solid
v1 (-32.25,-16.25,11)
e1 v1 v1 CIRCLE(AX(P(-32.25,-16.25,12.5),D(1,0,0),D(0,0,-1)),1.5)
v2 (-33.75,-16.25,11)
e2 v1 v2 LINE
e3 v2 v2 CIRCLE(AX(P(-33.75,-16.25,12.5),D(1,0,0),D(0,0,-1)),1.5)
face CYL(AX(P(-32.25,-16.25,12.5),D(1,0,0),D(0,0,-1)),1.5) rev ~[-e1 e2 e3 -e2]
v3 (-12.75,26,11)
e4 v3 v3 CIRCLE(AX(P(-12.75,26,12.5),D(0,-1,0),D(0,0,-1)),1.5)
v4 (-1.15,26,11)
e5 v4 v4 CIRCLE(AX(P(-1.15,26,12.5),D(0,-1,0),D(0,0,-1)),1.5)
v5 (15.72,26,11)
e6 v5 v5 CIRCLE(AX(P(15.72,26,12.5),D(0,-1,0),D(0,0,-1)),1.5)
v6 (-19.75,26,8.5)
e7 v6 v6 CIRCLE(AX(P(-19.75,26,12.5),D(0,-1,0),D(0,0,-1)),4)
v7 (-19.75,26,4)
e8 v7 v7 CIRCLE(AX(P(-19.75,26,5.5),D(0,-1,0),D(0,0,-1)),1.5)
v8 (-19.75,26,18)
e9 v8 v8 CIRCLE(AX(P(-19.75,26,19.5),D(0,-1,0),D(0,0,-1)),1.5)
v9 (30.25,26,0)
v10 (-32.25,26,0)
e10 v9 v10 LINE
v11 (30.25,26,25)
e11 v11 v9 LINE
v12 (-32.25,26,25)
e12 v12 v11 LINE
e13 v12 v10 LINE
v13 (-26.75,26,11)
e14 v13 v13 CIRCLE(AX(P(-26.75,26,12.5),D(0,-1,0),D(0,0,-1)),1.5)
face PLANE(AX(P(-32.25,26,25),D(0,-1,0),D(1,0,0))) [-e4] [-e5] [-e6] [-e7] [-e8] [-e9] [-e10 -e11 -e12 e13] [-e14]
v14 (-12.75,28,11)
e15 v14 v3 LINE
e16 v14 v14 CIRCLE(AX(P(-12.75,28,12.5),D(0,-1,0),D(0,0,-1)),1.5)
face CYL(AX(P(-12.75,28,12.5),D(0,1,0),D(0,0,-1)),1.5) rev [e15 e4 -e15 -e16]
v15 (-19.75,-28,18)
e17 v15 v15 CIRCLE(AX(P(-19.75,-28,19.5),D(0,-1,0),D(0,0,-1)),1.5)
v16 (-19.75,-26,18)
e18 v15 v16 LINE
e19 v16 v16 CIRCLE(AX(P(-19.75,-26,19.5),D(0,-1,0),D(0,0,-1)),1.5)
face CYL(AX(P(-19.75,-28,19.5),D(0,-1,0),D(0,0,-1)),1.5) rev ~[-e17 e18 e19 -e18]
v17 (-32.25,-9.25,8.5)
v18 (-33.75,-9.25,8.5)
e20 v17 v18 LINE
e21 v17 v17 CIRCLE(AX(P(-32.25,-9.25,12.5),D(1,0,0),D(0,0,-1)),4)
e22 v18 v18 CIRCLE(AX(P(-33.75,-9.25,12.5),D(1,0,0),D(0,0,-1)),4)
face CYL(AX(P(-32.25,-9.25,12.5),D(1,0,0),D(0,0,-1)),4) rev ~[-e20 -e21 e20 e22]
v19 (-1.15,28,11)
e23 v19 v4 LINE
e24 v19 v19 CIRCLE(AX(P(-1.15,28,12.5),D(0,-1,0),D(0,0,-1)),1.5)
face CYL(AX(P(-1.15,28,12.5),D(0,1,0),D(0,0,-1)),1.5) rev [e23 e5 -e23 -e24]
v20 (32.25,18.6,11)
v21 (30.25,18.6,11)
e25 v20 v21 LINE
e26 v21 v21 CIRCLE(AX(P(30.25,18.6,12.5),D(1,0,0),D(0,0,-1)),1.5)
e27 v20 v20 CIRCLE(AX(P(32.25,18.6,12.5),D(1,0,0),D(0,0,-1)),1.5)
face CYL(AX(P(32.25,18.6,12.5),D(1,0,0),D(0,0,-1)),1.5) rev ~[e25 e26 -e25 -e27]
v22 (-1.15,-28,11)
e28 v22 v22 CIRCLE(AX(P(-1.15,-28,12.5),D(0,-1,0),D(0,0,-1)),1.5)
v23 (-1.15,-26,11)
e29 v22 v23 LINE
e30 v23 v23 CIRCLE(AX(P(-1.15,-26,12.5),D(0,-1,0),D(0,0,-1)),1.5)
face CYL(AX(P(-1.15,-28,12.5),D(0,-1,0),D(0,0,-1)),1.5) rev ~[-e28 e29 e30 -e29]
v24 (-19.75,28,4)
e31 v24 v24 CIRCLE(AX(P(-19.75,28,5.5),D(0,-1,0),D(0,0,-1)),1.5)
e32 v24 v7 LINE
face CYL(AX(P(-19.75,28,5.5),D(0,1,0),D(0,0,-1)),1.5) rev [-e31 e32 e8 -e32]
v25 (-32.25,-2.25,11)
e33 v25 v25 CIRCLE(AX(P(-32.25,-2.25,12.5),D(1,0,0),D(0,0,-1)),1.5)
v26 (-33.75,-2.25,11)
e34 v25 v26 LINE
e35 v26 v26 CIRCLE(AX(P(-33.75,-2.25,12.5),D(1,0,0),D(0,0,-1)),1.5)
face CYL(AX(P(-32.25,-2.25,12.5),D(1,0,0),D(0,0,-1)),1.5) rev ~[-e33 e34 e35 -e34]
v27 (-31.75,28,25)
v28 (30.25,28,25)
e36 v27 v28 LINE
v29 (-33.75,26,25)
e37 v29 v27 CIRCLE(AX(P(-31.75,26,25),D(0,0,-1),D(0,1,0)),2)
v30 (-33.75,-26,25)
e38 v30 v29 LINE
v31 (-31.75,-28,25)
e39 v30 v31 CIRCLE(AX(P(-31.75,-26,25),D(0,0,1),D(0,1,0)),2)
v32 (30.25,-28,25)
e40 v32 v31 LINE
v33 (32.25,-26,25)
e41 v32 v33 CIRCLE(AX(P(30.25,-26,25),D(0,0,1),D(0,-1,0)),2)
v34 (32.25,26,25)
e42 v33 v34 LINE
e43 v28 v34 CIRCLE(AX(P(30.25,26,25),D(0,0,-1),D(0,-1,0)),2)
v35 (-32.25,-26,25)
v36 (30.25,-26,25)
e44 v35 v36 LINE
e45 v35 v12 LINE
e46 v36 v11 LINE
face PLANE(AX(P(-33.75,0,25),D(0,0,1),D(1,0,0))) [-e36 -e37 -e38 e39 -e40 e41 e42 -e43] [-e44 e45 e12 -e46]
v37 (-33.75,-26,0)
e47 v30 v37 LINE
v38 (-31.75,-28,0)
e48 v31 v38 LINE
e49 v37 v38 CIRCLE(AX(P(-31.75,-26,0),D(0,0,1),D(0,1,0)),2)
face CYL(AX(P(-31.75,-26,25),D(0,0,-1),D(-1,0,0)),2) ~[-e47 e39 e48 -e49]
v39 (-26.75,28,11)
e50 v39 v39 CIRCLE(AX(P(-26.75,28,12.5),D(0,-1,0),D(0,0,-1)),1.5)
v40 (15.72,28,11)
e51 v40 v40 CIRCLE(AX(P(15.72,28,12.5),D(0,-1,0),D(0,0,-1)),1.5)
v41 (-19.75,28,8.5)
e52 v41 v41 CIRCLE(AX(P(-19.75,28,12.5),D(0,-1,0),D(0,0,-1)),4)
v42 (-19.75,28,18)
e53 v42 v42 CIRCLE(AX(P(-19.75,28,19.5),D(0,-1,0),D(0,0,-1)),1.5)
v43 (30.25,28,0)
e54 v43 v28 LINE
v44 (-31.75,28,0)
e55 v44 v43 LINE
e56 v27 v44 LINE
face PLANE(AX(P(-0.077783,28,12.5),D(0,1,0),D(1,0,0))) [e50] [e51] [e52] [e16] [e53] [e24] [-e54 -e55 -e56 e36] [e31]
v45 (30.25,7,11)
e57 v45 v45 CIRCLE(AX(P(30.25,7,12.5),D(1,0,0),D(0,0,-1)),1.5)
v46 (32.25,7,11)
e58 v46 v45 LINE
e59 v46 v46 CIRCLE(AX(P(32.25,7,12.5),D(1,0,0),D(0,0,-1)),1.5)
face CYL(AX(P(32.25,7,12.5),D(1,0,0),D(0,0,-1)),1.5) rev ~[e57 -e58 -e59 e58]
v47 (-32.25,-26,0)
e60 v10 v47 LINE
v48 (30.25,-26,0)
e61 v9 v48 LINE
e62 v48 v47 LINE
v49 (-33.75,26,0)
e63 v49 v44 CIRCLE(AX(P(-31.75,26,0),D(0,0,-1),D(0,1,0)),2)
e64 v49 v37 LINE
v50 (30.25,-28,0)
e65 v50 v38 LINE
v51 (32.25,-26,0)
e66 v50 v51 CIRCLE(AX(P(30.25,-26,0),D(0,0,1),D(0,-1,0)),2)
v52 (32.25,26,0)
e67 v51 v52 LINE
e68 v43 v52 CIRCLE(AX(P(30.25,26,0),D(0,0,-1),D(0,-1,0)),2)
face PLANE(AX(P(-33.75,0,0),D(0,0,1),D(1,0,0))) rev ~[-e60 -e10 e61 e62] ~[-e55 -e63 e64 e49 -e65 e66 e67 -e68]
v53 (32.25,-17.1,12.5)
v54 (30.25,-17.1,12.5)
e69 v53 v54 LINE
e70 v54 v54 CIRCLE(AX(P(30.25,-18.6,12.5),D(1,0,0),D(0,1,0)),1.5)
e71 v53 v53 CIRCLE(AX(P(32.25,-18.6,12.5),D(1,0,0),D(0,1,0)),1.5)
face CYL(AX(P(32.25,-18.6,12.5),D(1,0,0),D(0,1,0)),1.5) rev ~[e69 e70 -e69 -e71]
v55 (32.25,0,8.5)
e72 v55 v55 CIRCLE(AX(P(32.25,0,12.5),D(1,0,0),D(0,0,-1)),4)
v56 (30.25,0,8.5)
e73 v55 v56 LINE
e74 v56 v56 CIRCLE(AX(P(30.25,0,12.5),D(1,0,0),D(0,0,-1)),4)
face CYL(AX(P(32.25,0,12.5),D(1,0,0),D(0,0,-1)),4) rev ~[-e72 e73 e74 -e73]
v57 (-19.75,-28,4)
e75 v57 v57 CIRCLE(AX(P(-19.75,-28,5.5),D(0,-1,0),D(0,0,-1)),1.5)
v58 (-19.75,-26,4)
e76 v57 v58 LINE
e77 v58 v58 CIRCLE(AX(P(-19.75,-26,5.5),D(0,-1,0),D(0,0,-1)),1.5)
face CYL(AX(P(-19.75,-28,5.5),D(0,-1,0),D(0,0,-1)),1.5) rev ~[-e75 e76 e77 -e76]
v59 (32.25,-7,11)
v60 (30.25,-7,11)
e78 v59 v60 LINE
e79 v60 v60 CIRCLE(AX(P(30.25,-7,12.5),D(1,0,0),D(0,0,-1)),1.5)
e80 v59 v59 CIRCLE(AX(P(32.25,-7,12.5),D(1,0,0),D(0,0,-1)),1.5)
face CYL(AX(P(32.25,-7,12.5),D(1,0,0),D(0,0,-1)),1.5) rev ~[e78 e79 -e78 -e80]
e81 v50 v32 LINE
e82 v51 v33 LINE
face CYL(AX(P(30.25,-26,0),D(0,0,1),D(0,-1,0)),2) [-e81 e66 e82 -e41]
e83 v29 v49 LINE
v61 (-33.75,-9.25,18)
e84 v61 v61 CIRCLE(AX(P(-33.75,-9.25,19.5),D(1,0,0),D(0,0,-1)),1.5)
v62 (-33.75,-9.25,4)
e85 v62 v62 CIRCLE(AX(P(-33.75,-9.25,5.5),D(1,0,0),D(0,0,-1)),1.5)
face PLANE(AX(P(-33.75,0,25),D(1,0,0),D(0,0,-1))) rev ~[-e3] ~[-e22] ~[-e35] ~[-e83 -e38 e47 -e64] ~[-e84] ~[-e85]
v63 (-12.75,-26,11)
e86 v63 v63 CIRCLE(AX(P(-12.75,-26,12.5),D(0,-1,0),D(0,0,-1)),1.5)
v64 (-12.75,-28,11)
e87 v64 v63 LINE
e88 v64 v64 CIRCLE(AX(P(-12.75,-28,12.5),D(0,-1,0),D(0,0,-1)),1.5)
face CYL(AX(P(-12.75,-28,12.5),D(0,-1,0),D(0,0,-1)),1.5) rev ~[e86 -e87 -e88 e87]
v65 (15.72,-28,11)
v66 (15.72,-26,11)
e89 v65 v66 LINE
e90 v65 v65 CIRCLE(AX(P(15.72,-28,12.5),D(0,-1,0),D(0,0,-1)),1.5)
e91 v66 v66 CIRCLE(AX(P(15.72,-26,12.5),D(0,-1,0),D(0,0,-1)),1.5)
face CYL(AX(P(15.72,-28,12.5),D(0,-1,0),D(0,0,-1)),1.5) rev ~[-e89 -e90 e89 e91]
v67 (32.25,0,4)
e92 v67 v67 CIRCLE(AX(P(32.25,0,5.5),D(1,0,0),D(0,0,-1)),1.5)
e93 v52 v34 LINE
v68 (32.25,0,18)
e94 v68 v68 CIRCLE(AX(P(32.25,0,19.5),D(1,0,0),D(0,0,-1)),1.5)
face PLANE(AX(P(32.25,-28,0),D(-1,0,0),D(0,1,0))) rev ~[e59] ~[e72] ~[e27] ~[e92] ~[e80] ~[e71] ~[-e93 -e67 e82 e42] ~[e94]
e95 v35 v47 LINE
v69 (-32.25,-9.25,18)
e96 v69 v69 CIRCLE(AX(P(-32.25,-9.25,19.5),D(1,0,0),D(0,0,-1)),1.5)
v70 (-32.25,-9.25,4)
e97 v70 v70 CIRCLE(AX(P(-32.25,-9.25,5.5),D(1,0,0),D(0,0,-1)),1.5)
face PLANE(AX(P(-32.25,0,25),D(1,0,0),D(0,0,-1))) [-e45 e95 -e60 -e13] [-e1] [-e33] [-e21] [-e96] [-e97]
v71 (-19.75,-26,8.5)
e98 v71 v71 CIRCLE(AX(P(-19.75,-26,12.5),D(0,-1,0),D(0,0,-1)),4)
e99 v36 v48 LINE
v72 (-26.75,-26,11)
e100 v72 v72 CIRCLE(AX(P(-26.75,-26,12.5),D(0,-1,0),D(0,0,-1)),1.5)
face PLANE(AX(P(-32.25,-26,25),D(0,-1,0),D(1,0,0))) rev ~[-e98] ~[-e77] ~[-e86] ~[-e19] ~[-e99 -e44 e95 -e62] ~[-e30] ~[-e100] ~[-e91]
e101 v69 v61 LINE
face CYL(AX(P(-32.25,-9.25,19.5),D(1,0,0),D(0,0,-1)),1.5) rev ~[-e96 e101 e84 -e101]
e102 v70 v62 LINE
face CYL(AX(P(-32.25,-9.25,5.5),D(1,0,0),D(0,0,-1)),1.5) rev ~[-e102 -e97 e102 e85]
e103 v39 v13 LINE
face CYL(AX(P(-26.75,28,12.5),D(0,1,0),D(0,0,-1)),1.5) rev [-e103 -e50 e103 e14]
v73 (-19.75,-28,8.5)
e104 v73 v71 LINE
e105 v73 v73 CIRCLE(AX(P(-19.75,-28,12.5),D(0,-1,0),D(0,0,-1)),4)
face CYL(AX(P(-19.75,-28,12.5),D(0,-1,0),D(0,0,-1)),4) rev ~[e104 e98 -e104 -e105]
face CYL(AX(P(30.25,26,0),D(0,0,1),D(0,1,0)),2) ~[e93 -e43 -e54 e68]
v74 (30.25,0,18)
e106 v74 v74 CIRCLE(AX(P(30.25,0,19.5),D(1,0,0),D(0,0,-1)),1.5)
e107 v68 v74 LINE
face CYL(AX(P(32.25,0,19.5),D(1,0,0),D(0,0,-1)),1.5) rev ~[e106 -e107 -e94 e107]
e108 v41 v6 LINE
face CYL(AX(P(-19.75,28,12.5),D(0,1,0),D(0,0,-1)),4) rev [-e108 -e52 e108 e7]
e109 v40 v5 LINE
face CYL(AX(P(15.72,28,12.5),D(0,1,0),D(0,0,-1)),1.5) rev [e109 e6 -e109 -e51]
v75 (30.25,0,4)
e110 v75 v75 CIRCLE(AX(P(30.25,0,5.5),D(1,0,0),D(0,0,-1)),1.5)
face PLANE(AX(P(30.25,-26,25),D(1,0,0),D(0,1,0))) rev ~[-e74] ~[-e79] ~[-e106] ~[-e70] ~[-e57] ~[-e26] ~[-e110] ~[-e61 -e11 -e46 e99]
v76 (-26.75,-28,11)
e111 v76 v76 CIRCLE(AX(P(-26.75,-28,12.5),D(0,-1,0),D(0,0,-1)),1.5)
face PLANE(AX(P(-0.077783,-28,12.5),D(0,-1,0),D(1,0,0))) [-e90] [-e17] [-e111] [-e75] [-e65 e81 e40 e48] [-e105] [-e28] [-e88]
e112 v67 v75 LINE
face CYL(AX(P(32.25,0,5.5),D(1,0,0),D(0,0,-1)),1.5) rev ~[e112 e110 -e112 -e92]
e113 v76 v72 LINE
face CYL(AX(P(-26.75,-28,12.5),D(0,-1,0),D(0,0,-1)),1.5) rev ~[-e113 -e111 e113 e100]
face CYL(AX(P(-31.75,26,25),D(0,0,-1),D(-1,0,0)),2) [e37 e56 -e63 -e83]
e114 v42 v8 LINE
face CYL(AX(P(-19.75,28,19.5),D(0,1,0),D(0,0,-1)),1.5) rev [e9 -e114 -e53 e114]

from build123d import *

# Parameters (mm, degrees)
SKETCH1_W                       = 64.5
SKETCH1_H                       = 56
BOSS_EXTRUDE1_DEPTH             = 25
CUT_EXTRUDE1_REACH              = 51.488
SKETCH2_W                       = 62.5
SKETCH2_H                       = 52
CUT_EXTRUDE2_REACH              = 76.627
SKETCH3_R                       = 4
SKETCH3_R_2                     = 1.5
CUT_EXTRUDE3_REACH              = 71.29
SKETCH4_R                       = 4
SKETCH4_R_2                     = 1.5
FILLET3_R                       = 2
BOSS_EXTRUDE2_REACH             = 51.488
SKETCH5_W                       = 1.5
SKETCH5_H                       = 25
BOSS_EXTRUDE2_DIRECTION_2_REACH = 51.488
FILLET4_R                       = 2
SKETCH6_R                       = 1.5
SKETCH6_R_2                     = 4
CUT_EXTRUDE5_DEPTH              = 1.5


with BuildPart() as part:
    # Sketch1 → Boss-Extrude1 (new body)
    with BuildSketch(Plane.XY):
        Rectangle(SKETCH1_W, SKETCH1_H)
    extrude(amount=BOSS_EXTRUDE1_DEPTH)

    # Sketch2 → Cut-Extrude1 (cut, up to next)
    with BuildSketch(Plane.XY.offset(25), mode=Mode.PRIVATE) as cut_extrude1_sk1:
        with Locations((-1, 0)):
            Rectangle(SKETCH2_W, SKETCH2_H)
    cut_extrude1_tool1 = extrude(cut_extrude1_sk1.sketch, amount=-CUT_EXTRUDE1_REACH, mode=Mode.PRIVATE) & part.part
    add(cut_extrude1_tool1.solids().sort_by_distance((-1, 0, 25))[0], mode=Mode.SUBTRACT)

    # Sketch3 → Cut-Extrude2 (cut, up to next)
    with BuildSketch(Plane(origin=(32.25, 0, 0), x_dir=(0, 0, -1), z_dir=(1, 0, 0)), mode=Mode.PRIVATE) as cut_extrude2_sk1:
        with Locations((-12.5, 0)):
            Circle(SKETCH3_R)
    cut_extrude2_tool1 = extrude(cut_extrude2_sk1.sketch, amount=-CUT_EXTRUDE2_REACH, mode=Mode.PRIVATE) & part.part
    # Sketch3 → Cut-Extrude2 (cut, up to next)
    with BuildSketch(Plane(origin=(32.25, 0, 0), x_dir=(0, 0, -1), z_dir=(1, 0, 0)), mode=Mode.PRIVATE) as cut_extrude2_sk2:
        with Locations((-5.5, 0)):
            Circle(SKETCH3_R_2)
    cut_extrude2_tool2 = extrude(cut_extrude2_sk2.sketch, amount=-CUT_EXTRUDE2_REACH, mode=Mode.PRIVATE) & part.part
    # Sketch3 → Cut-Extrude2 (cut, up to next)
    with BuildSketch(Plane(origin=(32.25, 0, 0), x_dir=(0, 0, -1), z_dir=(1, 0, 0)), mode=Mode.PRIVATE) as cut_extrude2_sk3:
        with Locations((-12.5, 18.6)):
            Circle(SKETCH3_R_2)
    cut_extrude2_tool3 = extrude(cut_extrude2_sk3.sketch, amount=-CUT_EXTRUDE2_REACH, mode=Mode.PRIVATE) & part.part
    # Sketch3 → Cut-Extrude2 (cut, up to next)
    with BuildSketch(Plane(origin=(32.25, 0, 0), x_dir=(0, 0, -1), z_dir=(1, 0, 0)), mode=Mode.PRIVATE) as cut_extrude2_sk4:
        with Locations((-12.5, -7)):
            Circle(SKETCH3_R_2)
    cut_extrude2_tool4 = extrude(cut_extrude2_sk4.sketch, amount=-CUT_EXTRUDE2_REACH, mode=Mode.PRIVATE) & part.part
    # Sketch3 → Cut-Extrude2 (cut, up to next)
    with BuildSketch(Plane(origin=(32.25, 0, 0), x_dir=(0, 0, -1), z_dir=(1, 0, 0)), mode=Mode.PRIVATE) as cut_extrude2_sk5:
        with Locations((-19.5, 0)):
            Circle(SKETCH3_R_2)
    cut_extrude2_tool5 = extrude(cut_extrude2_sk5.sketch, amount=-CUT_EXTRUDE2_REACH, mode=Mode.PRIVATE) & part.part
    # Sketch3 → Cut-Extrude2 (cut, up to next)
    with BuildSketch(Plane(origin=(32.25, 0, 0), x_dir=(0, 0, -1), z_dir=(1, 0, 0)), mode=Mode.PRIVATE) as cut_extrude2_sk6:
        with Locations((-12.5, 7)):
            Circle(SKETCH3_R_2)
    cut_extrude2_tool6 = extrude(cut_extrude2_sk6.sketch, amount=-CUT_EXTRUDE2_REACH, mode=Mode.PRIVATE) & part.part
    # Sketch3 → Cut-Extrude2 (cut, up to next)
    with BuildSketch(Plane(origin=(32.25, 0, 0), x_dir=(0, 0, -1), z_dir=(1, 0, 0)), mode=Mode.PRIVATE) as cut_extrude2_sk7:
        with Locations(Location((-12.5, -18.6, 0), (0, 0, 90))):
            Circle(SKETCH3_R_2)
    cut_extrude2_tool7 = extrude(cut_extrude2_sk7.sketch, amount=-CUT_EXTRUDE2_REACH, mode=Mode.PRIVATE) & part.part
    add(cut_extrude2_tool1.solids().sort_by_distance((32.25, 0, 12.5))[0], mode=Mode.SUBTRACT)
    add(cut_extrude2_tool2.solids().sort_by_distance((32.25, 0, 5.5))[0], mode=Mode.SUBTRACT)
    add(cut_extrude2_tool3.solids().sort_by_distance((32.25, 18.6, 12.5))[0], mode=Mode.SUBTRACT)
    add(cut_extrude2_tool4.solids().sort_by_distance((32.25, -7, 12.5))[0], mode=Mode.SUBTRACT)
    add(cut_extrude2_tool5.solids().sort_by_distance((32.25, 0, 19.5))[0], mode=Mode.SUBTRACT)
    add(cut_extrude2_tool6.solids().sort_by_distance((32.25, 7, 12.5))[0], mode=Mode.SUBTRACT)
    add(cut_extrude2_tool7.solids().sort_by_distance((32.25, -18.6, 12.5))[0], mode=Mode.SUBTRACT)

    # Sketch4 → Cut-Extrude3 (cut, up to next)
    with BuildSketch(Plane.XZ.offset(28), mode=Mode.PRIVATE) as cut_extrude3_sk1:
        with Locations(Location((-19.75, 12.5, 0), (0, 0, 270))):
            Circle(SKETCH4_R)
    cut_extrude3_tool1 = extrude(cut_extrude3_sk1.sketch, amount=-CUT_EXTRUDE3_REACH, mode=Mode.PRIVATE) & part.part
    # Sketch4 → Cut-Extrude3 (cut, up to next)
    with BuildSketch(Plane.XZ.offset(28), mode=Mode.PRIVATE) as cut_extrude3_sk2:
        with Locations(Location((-12.75, 12.5, 0), (0, 0, 270))):
            Circle(SKETCH4_R_2)
    cut_extrude3_tool2 = extrude(cut_extrude3_sk2.sketch, amount=-CUT_EXTRUDE3_REACH, mode=Mode.PRIVATE) & part.part
    # Sketch4 → Cut-Extrude3 (cut, up to next)
    with BuildSketch(Plane.XZ.offset(28), mode=Mode.PRIVATE) as cut_extrude3_sk3:
        with Locations(Location((-1.15, 12.5, 0), (0, 0, 270))):
            Circle(SKETCH4_R_2)
    cut_extrude3_tool3 = extrude(cut_extrude3_sk3.sketch, amount=-CUT_EXTRUDE3_REACH, mode=Mode.PRIVATE) & part.part
    # Sketch4 → Cut-Extrude3 (cut, up to next)
    with BuildSketch(Plane.XZ.offset(28), mode=Mode.PRIVATE) as cut_extrude3_sk4:
        with Locations(Location((15.72, 12.5, 0), (0, 0, 270))):
            Circle(SKETCH4_R_2)
    cut_extrude3_tool4 = extrude(cut_extrude3_sk4.sketch, amount=-CUT_EXTRUDE3_REACH, mode=Mode.PRIVATE) & part.part
    # Sketch4 → Cut-Extrude3 (cut, up to next)
    with BuildSketch(Plane.XZ.offset(28), mode=Mode.PRIVATE) as cut_extrude3_sk5:
        with Locations(Location((-19.75, 5.5, 0), (0, 0, 270))):
            Circle(SKETCH4_R_2)
    cut_extrude3_tool5 = extrude(cut_extrude3_sk5.sketch, amount=-CUT_EXTRUDE3_REACH, mode=Mode.PRIVATE) & part.part
    # Sketch4 → Cut-Extrude3 (cut, up to next)
    with BuildSketch(Plane.XZ.offset(28), mode=Mode.PRIVATE) as cut_extrude3_sk6:
        with Locations(Location((-26.75, 12.5, 0), (0, 0, 270))):
            Circle(SKETCH4_R_2)
    cut_extrude3_tool6 = extrude(cut_extrude3_sk6.sketch, amount=-CUT_EXTRUDE3_REACH, mode=Mode.PRIVATE) & part.part
    # Sketch4 → Cut-Extrude3 (cut, up to next)
    with BuildSketch(Plane.XZ.offset(28), mode=Mode.PRIVATE) as cut_extrude3_sk7:
        with Locations(Location((-19.75, 19.5, 0), (0, 0, 270))):
            Circle(SKETCH4_R_2)
    cut_extrude3_tool7 = extrude(cut_extrude3_sk7.sketch, amount=-CUT_EXTRUDE3_REACH, mode=Mode.PRIVATE) & part.part
    cut_extrude3_1 = cut_extrude3_tool1.solids().sort_by_distance((-19.75, -28, 12.5))[0]
    add(cut_extrude3_1, mode=Mode.SUBTRACT)
    cut_extrude3_2 = cut_extrude3_tool2.solids().sort_by_distance((-12.75, -28, 12.5))[0]
    add(cut_extrude3_2, mode=Mode.SUBTRACT)
    cut_extrude3_3 = cut_extrude3_tool3.solids().sort_by_distance((-1.15, -28, 12.5))[0]
    add(cut_extrude3_3, mode=Mode.SUBTRACT)
    cut_extrude3_4 = cut_extrude3_tool4.solids().sort_by_distance((15.72, -28, 12.5))[0]
    add(cut_extrude3_4, mode=Mode.SUBTRACT)
    cut_extrude3_5 = cut_extrude3_tool5.solids().sort_by_distance((-19.75, -28, 5.5))[0]
    add(cut_extrude3_5, mode=Mode.SUBTRACT)
    cut_extrude3_6 = cut_extrude3_tool6.solids().sort_by_distance((-26.75, -28, 12.5))[0]
    add(cut_extrude3_6, mode=Mode.SUBTRACT)
    cut_extrude3_7 = cut_extrude3_tool7.solids().sort_by_distance((-19.75, -28, 19.5))[0]
    add(cut_extrude3_7, mode=Mode.SUBTRACT)
    cut_extrude3 = cut_extrude3_1 + cut_extrude3_2 + cut_extrude3_3 + cut_extrude3_4 + cut_extrude3_5 + cut_extrude3_6 + cut_extrude3_7  # Cut-Extrude3 as one shape, for the pattern or mirror that repeats it

    # Mirror1: Cut-Extrude3 across plane
    add(cut_extrude3.mirror(Plane.ZX), mode=Mode.SUBTRACT)

    # Fillet3
    fillet3_edges = [part.edges().sort_by_distance(p)[0] for p in [
        (32.25, -28, 12.5),
        (32.25, 28, 12.5),
    ]]
    fillet(fillet3_edges, radius=FILLET3_R)

    # Boss-Extrude2: up to this face of the body (flat: up to its plane)
    boss_extrude2_end = Plane(part.part.faces().sort_by_distance((-1, 28, 0.673145601))[0])
    # Sketch5 → Boss-Extrude2 (add, up to the picked face)
    with BuildSketch(Plane(origin=(0, 0, 0), x_dir=(1, 0, 0), z_dir=(0, 1, 0)), mode=Mode.PRIVATE) as boss_extrude2_sk1:
        with Locations((-33, -12.5)):
            Rectangle(SKETCH5_W, SKETCH5_H)
    boss_extrude2_tool1 = split(extrude(boss_extrude2_sk1.sketch, amount=BOSS_EXTRUDE2_REACH, mode=Mode.PRIVATE), bisect_by=boss_extrude2_end, keep=Keep.BOTH, mode=Mode.PRIVATE)
    add(boss_extrude2_tool1.solids().sort_by(Axis((-33, 0, 12.5), (0, 1, 0)))[0])

    # Boss-Extrude2 direction 2: up to this face of the body (flat: up to its plane)
    boss_extrude2_direction_2_end = Plane(part.part.faces().sort_by_distance((-1, -28, 0.673145601))[0])
    # Sketch5 → Boss-Extrude2 direction 2 (add, up to the picked face)
    with BuildSketch(Plane(origin=(0, 0, 0), x_dir=(1, 0, 0), z_dir=(0, 1, 0)), mode=Mode.PRIVATE) as boss_extrude2_direction_2_sk1:
        with Locations((-33, -12.5)):
            Rectangle(SKETCH5_W, SKETCH5_H)
    boss_extrude2_direction_2_tool1 = split(extrude(boss_extrude2_direction_2_sk1.sketch, amount=-BOSS_EXTRUDE2_DIRECTION_2_REACH, mode=Mode.PRIVATE), bisect_by=boss_extrude2_direction_2_end, keep=Keep.BOTH, mode=Mode.PRIVATE)
    add(boss_extrude2_direction_2_tool1.solids().sort_by(Axis((-33, 0, 12.5), (0, -1, 0)))[0])

    # Fillet4
    fillet4_edges = [part.edges().sort_by_distance(p)[0] for p in [
        (-33.75, 28, 12.5),
        (-33.75, -28, 12.5),
    ]]
    fillet(fillet4_edges, radius=FILLET4_R)

    # Sketch6 → Cut-Extrude5 (cut)
    with BuildSketch(Plane(origin=(-32.25, 0, 0), x_dir=(0, 0, -1), z_dir=(1, 0, 0))):
        with Locations((-12.5, -2.25)):
            Circle(SKETCH6_R)
        with Locations((-19.5, -9.25)):
            Circle(SKETCH6_R)
        with Locations((-5.5, -9.25)):
            Circle(SKETCH6_R)
        with Locations((-12.5, -16.25)):
            Circle(SKETCH6_R)
        with Locations((-12.5, -9.25)):
            Circle(SKETCH6_R_2)
    extrude(amount=-CUT_EXTRUDE5_DEPTH, mode=Mode.SUBTRACT)


solid = part.part
